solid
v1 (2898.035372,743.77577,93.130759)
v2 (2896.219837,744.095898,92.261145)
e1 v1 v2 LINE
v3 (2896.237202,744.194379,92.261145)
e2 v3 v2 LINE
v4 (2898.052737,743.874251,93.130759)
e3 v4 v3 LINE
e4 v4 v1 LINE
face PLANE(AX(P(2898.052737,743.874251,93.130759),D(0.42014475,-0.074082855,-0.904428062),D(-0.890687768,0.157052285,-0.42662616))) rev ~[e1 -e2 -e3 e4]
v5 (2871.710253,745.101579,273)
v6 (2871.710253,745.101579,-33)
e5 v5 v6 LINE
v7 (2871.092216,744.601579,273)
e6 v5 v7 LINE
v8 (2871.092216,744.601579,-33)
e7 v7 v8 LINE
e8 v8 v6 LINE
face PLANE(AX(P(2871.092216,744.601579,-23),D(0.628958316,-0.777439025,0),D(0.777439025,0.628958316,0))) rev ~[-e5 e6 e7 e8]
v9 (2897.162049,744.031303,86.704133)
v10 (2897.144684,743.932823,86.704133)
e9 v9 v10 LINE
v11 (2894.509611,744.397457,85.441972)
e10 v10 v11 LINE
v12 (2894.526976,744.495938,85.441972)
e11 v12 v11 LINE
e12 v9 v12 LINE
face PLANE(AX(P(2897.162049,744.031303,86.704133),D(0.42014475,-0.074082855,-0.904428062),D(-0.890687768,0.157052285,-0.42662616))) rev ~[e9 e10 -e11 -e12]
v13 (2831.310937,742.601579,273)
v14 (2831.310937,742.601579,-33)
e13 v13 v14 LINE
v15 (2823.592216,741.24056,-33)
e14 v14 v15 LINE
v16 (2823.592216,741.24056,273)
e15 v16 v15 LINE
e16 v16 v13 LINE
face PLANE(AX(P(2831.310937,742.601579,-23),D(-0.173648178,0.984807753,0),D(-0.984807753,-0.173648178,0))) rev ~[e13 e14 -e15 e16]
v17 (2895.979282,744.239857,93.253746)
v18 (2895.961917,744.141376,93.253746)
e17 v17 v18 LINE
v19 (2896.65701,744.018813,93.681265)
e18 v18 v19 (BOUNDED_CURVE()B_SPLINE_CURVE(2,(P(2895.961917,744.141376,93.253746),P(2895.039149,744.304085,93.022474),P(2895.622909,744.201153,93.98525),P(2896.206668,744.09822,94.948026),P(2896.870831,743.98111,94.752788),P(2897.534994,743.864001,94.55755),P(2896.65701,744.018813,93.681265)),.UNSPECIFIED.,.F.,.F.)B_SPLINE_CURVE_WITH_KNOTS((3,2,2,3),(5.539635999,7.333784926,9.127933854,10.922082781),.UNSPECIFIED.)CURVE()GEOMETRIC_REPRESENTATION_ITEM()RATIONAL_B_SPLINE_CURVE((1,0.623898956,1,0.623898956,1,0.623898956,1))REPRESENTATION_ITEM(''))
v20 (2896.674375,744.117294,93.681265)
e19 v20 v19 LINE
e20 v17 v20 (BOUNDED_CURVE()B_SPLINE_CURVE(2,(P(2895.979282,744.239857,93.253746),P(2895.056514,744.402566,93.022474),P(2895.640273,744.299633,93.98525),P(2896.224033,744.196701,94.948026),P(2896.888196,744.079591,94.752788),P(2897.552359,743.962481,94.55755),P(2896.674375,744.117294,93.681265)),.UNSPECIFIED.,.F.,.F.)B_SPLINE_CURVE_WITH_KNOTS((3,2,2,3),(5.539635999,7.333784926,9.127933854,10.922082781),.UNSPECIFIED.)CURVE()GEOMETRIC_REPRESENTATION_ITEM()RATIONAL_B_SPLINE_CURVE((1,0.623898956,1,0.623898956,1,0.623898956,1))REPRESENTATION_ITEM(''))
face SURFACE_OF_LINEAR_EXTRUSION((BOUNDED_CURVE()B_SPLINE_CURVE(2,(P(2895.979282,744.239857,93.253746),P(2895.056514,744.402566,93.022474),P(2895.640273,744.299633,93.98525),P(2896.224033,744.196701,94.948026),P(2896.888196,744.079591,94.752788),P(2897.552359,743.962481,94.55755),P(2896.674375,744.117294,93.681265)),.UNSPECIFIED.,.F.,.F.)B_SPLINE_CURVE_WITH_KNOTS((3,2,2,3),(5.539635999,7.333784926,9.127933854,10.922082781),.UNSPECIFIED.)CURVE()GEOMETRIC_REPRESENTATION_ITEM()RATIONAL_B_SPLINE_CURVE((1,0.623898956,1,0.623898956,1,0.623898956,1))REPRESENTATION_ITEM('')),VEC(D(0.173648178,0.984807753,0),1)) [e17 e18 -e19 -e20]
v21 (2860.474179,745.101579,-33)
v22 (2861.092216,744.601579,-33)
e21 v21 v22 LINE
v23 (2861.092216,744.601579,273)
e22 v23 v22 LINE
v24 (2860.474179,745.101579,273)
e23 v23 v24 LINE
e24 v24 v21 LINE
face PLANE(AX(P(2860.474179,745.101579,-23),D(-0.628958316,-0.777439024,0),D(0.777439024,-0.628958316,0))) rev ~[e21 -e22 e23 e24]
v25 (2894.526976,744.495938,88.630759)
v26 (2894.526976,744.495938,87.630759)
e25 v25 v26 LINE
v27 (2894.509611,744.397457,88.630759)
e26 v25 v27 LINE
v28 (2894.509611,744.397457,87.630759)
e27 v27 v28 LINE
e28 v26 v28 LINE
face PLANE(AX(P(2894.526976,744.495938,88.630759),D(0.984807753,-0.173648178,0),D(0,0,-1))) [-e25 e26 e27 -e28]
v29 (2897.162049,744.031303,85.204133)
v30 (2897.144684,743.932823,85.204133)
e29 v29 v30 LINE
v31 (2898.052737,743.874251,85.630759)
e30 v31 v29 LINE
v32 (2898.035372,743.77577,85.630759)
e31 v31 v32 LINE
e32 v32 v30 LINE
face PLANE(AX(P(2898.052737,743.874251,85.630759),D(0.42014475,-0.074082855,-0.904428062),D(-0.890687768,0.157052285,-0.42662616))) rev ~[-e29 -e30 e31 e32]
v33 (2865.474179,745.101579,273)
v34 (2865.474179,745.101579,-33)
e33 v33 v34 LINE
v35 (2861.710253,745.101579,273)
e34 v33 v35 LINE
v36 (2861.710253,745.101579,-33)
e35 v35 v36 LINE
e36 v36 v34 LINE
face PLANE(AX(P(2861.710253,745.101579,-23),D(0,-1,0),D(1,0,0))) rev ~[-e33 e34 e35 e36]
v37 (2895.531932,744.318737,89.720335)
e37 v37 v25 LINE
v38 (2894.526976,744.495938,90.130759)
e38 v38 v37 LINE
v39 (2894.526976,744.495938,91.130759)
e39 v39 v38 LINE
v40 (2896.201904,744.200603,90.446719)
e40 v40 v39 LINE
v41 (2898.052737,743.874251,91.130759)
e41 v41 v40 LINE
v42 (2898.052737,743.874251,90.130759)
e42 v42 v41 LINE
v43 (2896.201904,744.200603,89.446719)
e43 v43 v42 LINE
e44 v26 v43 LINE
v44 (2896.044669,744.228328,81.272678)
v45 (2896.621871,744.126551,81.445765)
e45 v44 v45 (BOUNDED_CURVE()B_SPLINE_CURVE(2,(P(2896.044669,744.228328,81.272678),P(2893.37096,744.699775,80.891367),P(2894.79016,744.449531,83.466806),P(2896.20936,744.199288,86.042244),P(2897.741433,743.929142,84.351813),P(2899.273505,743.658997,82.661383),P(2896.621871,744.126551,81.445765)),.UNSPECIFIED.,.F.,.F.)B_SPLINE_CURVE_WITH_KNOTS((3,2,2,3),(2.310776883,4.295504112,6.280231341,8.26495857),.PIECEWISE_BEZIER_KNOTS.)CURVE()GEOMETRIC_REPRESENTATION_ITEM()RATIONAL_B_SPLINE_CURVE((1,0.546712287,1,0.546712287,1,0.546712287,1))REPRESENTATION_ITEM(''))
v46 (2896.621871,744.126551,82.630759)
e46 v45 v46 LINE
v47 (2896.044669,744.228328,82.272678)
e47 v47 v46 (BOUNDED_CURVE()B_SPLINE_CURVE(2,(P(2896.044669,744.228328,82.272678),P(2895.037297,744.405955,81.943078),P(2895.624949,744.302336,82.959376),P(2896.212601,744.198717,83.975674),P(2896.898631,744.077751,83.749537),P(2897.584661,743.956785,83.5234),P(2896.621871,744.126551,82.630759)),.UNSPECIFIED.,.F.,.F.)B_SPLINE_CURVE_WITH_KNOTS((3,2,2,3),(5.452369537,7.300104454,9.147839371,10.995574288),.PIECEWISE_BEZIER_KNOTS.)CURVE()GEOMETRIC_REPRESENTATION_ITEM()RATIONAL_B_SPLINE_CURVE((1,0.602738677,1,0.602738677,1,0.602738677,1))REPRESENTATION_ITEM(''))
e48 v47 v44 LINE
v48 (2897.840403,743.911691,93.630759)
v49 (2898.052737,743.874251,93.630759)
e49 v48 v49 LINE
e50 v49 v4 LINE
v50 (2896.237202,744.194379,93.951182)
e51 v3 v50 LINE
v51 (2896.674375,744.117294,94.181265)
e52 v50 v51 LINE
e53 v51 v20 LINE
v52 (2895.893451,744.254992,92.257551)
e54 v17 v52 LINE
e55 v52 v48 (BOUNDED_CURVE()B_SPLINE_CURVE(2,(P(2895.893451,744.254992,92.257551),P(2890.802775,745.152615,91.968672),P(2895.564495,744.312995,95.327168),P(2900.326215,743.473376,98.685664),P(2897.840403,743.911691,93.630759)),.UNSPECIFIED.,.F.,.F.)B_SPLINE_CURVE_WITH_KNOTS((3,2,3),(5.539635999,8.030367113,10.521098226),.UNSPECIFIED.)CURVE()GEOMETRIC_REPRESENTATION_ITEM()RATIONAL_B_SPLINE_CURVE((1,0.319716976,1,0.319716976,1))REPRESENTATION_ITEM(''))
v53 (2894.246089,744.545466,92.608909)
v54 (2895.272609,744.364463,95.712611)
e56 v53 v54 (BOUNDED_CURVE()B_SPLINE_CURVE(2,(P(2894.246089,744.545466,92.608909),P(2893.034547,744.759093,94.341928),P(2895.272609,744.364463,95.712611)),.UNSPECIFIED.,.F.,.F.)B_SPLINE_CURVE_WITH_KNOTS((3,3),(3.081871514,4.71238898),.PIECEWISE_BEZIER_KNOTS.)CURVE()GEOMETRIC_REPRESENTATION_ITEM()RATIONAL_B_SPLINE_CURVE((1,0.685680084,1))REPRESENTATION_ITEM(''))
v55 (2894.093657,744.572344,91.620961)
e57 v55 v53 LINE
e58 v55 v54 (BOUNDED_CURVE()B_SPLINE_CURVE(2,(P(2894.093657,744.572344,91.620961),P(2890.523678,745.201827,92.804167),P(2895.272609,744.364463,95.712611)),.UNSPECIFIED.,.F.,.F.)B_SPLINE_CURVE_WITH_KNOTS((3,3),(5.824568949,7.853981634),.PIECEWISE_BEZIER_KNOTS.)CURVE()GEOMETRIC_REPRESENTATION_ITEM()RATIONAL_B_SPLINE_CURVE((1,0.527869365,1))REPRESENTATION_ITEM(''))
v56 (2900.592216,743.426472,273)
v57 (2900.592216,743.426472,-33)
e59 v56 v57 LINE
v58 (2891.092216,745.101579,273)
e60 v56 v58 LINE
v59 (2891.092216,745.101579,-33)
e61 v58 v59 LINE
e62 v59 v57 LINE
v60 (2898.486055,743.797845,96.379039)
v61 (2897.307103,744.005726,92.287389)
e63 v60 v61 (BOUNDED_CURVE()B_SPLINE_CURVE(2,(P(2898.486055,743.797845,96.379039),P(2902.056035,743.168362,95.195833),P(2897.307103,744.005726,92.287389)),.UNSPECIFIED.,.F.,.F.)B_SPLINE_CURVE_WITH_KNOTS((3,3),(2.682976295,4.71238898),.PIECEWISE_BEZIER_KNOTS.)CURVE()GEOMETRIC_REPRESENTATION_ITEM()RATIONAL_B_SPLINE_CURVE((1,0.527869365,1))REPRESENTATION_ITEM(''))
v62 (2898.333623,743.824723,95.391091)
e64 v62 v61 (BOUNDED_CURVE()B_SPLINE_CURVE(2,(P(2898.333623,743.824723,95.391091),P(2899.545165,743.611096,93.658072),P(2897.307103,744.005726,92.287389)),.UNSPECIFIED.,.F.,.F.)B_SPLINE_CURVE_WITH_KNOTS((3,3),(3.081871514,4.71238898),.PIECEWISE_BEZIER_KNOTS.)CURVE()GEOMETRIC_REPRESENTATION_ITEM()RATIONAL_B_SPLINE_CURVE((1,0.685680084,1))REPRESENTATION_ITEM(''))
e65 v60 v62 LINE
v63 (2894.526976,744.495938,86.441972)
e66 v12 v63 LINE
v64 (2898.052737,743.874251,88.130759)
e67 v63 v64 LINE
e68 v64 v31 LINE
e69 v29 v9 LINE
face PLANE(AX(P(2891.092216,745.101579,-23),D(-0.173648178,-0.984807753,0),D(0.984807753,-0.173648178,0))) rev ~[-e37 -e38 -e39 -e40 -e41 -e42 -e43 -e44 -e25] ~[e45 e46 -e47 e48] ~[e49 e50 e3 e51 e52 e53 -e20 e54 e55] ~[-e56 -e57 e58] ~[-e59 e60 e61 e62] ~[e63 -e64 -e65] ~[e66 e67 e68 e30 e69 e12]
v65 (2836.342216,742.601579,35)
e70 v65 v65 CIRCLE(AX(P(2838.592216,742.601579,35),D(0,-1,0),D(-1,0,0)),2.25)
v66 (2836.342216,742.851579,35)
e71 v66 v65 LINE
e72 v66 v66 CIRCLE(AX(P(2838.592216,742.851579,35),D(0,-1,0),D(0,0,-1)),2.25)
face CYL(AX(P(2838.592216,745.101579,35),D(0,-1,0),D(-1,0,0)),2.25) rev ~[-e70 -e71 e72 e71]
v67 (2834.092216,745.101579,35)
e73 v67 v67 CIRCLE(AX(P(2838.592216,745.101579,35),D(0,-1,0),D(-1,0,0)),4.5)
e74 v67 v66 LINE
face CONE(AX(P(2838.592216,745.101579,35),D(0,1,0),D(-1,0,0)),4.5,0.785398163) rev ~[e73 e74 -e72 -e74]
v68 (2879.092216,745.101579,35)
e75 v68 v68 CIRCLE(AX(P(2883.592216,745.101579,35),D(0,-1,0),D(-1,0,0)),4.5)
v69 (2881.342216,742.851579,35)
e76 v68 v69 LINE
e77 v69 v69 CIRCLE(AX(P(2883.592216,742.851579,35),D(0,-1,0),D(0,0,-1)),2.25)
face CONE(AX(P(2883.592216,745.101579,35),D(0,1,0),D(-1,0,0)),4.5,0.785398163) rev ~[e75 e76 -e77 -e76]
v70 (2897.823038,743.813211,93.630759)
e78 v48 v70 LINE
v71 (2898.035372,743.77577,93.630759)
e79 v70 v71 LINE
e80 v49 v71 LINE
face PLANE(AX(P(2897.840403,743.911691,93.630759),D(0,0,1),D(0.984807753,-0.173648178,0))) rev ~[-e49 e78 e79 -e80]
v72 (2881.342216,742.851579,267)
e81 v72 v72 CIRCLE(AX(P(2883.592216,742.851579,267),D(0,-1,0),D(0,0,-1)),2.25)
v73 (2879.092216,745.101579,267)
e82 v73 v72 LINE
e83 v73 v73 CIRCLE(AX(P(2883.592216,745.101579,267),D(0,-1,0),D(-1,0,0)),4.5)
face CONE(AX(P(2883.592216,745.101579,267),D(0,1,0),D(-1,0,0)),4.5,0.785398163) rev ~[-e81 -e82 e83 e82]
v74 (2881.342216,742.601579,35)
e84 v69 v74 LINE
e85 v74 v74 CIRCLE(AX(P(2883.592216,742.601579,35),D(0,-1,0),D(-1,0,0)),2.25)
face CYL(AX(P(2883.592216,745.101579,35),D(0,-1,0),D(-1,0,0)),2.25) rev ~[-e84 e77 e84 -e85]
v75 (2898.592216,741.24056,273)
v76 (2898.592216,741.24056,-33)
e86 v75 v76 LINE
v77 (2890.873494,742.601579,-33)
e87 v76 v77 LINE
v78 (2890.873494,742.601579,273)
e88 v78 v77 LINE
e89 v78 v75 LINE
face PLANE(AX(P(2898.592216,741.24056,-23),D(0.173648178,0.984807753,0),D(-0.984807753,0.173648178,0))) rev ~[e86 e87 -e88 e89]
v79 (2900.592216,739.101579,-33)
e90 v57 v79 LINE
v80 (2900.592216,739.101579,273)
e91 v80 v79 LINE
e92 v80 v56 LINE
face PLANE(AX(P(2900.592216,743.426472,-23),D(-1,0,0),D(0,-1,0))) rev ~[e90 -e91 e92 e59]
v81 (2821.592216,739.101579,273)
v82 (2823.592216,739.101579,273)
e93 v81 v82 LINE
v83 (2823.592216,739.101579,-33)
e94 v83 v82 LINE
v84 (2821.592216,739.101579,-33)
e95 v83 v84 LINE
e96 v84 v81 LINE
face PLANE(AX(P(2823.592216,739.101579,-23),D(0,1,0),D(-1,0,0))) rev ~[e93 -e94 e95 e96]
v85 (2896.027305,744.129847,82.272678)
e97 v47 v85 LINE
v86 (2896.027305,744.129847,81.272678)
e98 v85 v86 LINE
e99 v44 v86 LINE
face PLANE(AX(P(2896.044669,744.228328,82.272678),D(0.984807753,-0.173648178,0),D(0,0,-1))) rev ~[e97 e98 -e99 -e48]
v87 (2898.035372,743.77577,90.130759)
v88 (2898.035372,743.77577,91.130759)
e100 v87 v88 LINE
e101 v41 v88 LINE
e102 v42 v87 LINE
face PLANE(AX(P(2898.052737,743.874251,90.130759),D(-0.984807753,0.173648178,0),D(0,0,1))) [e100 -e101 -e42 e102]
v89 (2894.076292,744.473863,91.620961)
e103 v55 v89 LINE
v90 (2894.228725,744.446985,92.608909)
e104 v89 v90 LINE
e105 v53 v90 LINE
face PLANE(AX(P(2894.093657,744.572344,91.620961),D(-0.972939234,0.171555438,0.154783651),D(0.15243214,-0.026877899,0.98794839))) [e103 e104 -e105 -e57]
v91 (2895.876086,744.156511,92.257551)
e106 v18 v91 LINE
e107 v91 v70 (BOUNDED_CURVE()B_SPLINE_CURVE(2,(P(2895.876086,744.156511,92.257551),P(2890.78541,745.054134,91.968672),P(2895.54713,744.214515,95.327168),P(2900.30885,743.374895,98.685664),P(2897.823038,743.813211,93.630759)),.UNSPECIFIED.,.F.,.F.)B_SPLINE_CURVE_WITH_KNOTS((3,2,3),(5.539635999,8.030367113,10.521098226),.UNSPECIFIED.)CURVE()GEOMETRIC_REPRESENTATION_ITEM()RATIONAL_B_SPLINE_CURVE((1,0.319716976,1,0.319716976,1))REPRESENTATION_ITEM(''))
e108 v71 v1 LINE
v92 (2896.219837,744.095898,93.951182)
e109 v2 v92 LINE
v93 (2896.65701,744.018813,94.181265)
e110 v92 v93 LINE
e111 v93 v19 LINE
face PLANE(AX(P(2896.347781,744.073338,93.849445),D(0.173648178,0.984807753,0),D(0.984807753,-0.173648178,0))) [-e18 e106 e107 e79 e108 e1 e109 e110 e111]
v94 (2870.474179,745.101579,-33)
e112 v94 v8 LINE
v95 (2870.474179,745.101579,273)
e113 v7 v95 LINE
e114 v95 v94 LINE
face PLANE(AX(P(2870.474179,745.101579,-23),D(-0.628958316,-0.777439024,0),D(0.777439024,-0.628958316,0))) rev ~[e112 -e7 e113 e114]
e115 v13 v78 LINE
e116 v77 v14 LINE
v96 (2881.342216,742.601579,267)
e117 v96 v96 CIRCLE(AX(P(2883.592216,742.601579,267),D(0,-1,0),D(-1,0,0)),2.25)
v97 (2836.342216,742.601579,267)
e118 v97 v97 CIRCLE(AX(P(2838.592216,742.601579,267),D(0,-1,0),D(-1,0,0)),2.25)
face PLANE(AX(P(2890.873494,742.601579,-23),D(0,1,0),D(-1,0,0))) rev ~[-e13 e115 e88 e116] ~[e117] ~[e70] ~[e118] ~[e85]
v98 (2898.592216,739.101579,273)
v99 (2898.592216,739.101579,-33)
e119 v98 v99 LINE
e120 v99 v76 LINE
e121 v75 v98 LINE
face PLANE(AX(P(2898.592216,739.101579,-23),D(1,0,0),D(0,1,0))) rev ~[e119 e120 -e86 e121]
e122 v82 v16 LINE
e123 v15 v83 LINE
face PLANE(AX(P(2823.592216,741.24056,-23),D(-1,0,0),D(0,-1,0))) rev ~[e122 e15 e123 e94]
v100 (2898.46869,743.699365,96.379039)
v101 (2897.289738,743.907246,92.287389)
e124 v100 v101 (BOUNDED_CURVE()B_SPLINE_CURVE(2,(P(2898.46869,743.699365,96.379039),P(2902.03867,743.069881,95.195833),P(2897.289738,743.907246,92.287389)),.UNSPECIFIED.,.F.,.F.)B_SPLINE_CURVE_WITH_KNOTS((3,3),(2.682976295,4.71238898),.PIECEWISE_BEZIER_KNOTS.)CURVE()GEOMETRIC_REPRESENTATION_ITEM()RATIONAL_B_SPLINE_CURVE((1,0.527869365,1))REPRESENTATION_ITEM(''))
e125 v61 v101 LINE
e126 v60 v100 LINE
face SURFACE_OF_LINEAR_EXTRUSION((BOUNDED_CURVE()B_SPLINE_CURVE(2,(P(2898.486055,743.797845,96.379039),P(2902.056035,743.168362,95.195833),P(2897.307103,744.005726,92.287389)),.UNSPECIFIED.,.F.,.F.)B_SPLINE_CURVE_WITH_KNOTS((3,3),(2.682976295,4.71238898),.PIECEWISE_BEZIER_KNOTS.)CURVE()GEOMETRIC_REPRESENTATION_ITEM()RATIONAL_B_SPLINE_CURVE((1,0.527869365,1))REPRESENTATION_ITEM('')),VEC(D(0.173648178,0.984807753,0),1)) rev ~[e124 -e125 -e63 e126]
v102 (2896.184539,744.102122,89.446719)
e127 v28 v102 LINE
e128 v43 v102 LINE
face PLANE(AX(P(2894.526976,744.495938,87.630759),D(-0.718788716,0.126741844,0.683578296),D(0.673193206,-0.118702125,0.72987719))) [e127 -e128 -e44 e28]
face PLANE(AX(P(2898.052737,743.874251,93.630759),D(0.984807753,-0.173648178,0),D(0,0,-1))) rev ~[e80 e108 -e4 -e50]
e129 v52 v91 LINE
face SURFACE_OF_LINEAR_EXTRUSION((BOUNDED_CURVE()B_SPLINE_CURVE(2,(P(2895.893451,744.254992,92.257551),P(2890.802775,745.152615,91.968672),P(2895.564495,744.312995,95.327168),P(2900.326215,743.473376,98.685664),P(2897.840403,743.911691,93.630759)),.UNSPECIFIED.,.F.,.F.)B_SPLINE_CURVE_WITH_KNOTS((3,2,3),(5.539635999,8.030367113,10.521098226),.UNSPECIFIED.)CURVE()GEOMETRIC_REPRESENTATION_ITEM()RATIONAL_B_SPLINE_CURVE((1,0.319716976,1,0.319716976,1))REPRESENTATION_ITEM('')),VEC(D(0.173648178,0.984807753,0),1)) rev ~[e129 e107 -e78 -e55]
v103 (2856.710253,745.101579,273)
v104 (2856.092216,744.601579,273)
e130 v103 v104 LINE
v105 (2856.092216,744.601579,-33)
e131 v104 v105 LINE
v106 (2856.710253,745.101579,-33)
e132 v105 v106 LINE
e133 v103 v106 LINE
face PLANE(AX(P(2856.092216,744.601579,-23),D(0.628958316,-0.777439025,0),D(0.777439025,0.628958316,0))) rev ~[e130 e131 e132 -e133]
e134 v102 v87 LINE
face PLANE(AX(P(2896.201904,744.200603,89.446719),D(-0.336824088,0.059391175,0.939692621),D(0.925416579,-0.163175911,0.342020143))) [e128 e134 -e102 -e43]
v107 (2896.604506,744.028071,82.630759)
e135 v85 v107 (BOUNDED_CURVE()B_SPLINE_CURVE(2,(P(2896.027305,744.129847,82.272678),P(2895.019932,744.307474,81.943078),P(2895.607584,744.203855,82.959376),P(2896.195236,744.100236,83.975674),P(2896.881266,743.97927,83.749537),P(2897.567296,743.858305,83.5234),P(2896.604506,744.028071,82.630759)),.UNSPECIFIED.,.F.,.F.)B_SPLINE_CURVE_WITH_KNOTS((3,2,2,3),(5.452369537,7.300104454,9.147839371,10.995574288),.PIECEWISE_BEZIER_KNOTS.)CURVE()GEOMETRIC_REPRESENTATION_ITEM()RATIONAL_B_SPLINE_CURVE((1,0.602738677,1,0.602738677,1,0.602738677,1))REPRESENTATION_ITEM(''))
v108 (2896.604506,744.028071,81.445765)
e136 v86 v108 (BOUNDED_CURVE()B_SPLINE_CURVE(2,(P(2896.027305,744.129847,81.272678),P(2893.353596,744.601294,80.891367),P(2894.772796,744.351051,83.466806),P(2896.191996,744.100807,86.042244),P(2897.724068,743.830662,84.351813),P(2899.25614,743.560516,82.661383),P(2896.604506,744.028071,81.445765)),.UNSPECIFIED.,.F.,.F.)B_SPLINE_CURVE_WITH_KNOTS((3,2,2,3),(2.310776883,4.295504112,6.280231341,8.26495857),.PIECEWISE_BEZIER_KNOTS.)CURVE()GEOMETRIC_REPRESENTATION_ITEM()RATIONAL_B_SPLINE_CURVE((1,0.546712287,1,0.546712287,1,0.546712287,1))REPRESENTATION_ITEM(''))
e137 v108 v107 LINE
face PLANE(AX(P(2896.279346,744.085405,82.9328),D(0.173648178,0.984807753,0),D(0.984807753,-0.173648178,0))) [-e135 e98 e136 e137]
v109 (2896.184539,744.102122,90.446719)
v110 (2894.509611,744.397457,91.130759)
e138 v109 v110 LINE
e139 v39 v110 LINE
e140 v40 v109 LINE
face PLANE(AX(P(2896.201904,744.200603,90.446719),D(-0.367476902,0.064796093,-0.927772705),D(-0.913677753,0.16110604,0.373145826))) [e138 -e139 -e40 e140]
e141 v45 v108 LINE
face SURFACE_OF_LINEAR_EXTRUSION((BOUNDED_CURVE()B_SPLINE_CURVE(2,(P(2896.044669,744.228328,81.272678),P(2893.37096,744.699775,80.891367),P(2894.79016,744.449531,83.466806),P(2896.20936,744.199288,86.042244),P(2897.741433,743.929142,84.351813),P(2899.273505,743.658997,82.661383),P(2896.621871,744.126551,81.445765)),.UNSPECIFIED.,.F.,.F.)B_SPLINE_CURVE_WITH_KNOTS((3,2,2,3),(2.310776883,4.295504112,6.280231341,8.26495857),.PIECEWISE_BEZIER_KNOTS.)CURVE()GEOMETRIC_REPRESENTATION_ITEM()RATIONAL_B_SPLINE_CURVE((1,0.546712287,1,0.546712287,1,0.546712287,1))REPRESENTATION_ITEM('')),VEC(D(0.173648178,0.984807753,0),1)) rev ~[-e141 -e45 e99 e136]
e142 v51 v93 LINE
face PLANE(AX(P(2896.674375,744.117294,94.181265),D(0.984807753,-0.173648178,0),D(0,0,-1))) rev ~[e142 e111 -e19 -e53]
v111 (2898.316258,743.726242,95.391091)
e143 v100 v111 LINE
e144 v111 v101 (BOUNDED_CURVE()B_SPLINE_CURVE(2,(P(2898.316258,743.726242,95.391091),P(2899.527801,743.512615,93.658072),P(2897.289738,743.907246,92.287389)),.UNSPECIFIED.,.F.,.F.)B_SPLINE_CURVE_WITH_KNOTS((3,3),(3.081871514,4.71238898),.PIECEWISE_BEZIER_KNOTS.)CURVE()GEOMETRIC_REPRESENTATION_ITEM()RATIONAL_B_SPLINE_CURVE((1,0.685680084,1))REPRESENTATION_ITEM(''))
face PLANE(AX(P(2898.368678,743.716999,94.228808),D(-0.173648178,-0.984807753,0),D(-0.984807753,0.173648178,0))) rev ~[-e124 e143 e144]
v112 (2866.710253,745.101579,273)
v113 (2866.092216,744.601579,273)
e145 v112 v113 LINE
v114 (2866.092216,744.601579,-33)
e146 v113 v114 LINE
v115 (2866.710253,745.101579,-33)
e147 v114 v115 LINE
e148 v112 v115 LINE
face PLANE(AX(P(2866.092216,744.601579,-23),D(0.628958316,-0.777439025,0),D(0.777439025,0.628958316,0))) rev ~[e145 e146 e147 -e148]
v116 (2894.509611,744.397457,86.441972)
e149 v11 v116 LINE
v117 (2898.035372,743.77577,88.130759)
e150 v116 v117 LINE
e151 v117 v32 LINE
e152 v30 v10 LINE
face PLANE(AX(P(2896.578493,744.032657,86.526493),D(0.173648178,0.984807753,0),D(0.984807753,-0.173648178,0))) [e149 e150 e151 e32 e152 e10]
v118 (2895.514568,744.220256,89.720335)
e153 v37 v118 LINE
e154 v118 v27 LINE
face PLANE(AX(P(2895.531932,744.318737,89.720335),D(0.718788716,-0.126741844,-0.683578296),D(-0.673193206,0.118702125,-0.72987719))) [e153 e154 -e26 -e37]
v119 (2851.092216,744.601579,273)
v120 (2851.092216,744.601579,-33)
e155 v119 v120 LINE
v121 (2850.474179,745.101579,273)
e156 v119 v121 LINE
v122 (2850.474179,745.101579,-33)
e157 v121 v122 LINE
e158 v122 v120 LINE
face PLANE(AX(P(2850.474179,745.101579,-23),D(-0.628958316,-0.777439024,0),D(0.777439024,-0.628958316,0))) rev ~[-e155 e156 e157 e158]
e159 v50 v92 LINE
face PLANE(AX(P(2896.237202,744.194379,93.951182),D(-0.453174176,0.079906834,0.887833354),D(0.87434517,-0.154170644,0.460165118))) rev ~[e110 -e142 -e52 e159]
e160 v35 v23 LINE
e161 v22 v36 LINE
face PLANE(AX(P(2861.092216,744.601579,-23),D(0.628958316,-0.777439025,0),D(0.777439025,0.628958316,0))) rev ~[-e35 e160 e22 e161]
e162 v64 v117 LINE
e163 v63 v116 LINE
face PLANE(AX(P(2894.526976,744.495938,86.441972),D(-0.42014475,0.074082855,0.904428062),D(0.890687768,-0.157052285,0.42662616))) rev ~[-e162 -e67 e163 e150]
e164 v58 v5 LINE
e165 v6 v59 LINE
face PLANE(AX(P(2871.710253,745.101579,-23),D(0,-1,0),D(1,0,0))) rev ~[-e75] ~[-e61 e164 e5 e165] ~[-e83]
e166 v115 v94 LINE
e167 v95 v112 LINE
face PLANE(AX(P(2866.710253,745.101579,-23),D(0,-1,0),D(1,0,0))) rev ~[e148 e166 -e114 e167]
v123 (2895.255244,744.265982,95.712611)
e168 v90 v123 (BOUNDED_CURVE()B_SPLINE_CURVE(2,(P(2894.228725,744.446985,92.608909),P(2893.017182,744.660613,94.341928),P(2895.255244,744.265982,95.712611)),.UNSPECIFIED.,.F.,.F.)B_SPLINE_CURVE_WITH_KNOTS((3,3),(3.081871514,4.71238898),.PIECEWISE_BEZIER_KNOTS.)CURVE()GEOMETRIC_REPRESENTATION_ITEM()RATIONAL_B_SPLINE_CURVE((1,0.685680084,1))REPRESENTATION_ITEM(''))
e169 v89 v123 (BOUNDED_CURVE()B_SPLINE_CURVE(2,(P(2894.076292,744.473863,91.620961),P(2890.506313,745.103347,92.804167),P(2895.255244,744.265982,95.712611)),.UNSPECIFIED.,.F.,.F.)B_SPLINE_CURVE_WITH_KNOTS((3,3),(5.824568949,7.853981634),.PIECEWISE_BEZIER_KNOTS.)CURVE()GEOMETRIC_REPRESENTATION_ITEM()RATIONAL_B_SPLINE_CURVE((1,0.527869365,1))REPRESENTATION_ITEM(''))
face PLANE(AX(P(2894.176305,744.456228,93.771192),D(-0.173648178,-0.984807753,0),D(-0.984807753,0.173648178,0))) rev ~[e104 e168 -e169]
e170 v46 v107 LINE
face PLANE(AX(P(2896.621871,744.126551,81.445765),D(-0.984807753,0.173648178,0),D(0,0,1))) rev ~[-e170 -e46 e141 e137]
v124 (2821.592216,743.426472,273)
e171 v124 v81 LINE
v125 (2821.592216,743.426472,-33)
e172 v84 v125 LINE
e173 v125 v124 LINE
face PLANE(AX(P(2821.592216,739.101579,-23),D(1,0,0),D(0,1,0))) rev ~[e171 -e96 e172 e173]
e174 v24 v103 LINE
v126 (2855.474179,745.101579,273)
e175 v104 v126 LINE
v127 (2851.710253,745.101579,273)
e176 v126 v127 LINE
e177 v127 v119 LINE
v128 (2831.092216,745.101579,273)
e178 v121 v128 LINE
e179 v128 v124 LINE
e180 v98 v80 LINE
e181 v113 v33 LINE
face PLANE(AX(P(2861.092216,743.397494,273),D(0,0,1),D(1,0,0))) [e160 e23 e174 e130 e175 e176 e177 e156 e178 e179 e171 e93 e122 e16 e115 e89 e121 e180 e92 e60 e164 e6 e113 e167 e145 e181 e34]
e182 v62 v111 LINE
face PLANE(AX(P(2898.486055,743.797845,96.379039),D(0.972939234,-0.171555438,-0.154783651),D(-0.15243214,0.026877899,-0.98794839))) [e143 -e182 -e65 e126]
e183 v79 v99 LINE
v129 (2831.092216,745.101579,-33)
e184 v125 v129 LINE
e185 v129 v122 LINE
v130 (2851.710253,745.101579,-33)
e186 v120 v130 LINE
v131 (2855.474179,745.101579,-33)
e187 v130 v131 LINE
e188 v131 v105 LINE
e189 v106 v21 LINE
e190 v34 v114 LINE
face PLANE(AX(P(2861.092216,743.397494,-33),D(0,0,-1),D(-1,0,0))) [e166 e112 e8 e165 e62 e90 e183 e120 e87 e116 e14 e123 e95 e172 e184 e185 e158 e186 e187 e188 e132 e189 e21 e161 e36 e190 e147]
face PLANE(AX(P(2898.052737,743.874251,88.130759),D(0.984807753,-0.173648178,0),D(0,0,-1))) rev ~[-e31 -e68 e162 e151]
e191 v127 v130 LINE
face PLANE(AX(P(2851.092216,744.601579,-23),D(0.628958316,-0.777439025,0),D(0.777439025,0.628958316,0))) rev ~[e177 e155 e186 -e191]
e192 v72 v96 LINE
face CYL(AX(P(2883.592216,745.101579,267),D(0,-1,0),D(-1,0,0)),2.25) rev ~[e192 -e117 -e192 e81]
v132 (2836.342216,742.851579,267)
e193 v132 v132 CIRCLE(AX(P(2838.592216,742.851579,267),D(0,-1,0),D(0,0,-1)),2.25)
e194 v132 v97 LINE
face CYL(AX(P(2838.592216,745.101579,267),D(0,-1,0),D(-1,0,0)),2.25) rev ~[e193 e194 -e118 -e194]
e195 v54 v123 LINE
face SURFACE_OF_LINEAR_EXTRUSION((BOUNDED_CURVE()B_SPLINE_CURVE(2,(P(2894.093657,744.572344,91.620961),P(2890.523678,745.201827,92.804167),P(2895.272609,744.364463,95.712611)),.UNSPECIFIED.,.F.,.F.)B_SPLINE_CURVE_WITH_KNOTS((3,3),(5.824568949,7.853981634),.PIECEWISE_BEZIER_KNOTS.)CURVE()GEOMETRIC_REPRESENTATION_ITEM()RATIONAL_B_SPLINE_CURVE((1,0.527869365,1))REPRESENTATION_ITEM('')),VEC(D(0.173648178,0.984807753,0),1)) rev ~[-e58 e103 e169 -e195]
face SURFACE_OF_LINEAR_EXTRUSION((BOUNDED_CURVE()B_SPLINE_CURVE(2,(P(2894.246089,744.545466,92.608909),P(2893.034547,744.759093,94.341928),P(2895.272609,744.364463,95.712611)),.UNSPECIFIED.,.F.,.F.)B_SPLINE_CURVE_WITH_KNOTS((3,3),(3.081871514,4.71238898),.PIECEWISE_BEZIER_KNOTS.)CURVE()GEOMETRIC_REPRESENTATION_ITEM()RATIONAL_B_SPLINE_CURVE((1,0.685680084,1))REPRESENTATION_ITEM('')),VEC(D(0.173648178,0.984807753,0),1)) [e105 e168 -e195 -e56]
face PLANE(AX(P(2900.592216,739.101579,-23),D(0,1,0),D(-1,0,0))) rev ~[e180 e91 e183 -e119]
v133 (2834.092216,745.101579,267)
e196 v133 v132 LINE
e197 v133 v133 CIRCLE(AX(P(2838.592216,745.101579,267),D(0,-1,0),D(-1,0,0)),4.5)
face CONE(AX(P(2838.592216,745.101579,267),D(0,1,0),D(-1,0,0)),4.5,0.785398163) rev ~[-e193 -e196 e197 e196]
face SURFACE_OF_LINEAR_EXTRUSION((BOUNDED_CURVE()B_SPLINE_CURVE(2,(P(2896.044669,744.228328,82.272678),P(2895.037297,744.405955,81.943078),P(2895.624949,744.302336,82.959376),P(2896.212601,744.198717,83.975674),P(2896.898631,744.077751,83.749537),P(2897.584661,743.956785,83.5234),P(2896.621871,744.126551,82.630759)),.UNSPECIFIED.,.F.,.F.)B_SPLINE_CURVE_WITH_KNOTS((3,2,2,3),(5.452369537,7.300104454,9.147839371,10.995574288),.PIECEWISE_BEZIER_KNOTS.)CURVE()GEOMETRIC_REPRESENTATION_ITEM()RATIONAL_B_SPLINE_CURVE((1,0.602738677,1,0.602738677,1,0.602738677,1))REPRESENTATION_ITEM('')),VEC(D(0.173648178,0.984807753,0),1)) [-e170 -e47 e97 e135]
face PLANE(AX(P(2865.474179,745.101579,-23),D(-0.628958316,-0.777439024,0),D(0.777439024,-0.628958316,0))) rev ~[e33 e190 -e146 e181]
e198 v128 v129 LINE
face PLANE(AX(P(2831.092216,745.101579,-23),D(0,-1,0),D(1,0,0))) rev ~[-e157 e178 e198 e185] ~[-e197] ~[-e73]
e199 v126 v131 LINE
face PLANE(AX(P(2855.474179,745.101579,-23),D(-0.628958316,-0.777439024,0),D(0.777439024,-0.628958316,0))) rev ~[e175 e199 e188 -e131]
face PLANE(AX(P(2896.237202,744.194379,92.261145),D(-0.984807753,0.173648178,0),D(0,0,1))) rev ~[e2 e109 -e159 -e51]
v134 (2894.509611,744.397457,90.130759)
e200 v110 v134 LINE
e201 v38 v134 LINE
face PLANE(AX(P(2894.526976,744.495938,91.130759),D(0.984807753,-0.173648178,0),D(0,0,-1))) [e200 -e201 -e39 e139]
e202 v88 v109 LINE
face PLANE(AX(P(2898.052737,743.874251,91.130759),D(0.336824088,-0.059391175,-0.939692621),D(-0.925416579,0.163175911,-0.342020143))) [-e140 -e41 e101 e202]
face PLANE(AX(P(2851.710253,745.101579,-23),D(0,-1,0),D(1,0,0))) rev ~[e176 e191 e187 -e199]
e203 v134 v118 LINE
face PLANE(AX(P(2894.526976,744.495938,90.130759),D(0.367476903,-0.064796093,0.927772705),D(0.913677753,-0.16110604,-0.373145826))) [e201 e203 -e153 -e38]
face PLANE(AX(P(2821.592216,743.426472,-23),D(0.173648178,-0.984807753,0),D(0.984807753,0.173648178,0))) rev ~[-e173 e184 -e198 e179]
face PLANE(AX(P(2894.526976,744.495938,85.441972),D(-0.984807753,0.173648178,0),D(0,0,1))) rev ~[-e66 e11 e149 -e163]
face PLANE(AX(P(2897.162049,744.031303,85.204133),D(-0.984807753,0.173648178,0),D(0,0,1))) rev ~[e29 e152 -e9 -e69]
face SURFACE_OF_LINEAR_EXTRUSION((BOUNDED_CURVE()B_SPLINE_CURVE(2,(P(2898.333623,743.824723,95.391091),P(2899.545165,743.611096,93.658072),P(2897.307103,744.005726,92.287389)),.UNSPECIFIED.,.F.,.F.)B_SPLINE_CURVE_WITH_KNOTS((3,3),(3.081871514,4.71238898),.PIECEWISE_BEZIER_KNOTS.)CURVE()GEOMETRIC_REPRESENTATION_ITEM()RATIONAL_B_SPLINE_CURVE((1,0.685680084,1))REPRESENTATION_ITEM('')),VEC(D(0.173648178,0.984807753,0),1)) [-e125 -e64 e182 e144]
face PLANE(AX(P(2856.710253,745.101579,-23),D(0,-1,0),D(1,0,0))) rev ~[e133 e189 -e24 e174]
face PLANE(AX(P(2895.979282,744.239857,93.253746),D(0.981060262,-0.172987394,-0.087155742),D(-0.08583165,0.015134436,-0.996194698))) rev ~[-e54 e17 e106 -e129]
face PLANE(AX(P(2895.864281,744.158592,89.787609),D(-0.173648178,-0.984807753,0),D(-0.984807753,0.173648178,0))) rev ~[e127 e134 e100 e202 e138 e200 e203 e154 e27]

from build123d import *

# Parameters (mm, degrees)
EXTRUDE_1_DEPTH           = 250
CUT_EXTRUDE_1_DEPTH       = 0.1
EXTRUDE_2_DEPTH           = 23
EXTRUDE_3_DEPTH           = 23
HOLE_WIZARD_0_D           = 4.5
HOLE_WIZARD_0_CSINK_D     = 9
HOLE_WIZARD_0_CSINK_ANGLE = 90
EXTRUDE_4_DEPTH           = 10


with BuildPart() as part:
    # Model → 凸台-拉伸1 (new body)
    with BuildSketch(Plane.XY):
        Polygon((2831.092215663, 745.101578786), (2821.592215663, 743.426472469), (2821.592215663, 739.101578786), (2823.592215663, 739.101578786), (2823.592215663, 741.240559901), (2831.310937322, 742.601578786), (2890.873494004, 742.601578786), (2898.592215663, 741.240559901), (2898.592215663, 739.101578786), (2900.592215663, 739.101578786), (2900.592215663, 743.426472469), (2891.092215663, 745.101578786), (2871.710252666, 745.101578786), (2871.092215663, 744.601578786), (2870.474178661, 745.101578786), (2866.710252666, 745.101578786), (2866.092215663, 744.601578786), (2865.474178661, 745.101578786), (2861.710252666, 745.101578786), (2861.092215663, 744.601578786), (2860.474178661, 745.101578786), (2856.710252666, 745.101578786), (2856.092215663, 744.601578786), (2855.474178661, 745.101578786), (2851.710252666, 745.101578786), (2851.092215663, 744.601578786), (2850.474178661, 745.101578786), align=None)
    extrude(amount=EXTRUDE_1_DEPTH)

    # 草图1 → 切除-拉伸1 (cut)
    with BuildSketch(Plane(origin=(214.596971693, 1217.039904055, 0), x_dir=(0.9848077530109746, -0.1736481776739262, 0), z_dir=(0.17364817767392618, 0.9848077530109745, 0))):
        with BuildLine():
            Line((2722.813350585, -82.272677588), (2722.813350585, -81.272677588))
            add(Edge.make_bspline(
                [(2722.813350585, -81.272677588), (2720.098395425, -80.891367095), (2721.539488829, -83.466805597), (2722.980582232, -86.042244099), (2724.536289142, -84.351813392), (2726.091996051, -82.661382685), (2723.399456691, -81.445765021)],
                knots=[2.310776883, 2.310776883, 2.310776883, 4.295504112, 4.295504112, 6.280231341, 6.280231341, 8.26495857, 8.26495857, 8.26495857], degree=2, weights=[1, 0.546712287, 1, 0.546712287, 1, 0.546712287, 1]))
            Line((2723.399456691, -81.445765021), (2723.399456691, -82.630759165))
            add(Edge.make_bspline(
                [(2722.813350585, -82.272677588), (2721.79043745, -81.943078281), (2722.387154928, -82.959375958), (2722.983872407, -83.975673634), (2723.680485897, -83.749536627), (2724.377099386, -83.523399621), (2723.399456691, -82.630759165)],
                knots=[5.452369537, 5.452369537, 5.452369537, 7.300104454, 7.300104454, 9.147839371, 9.147839371, 10.995574288, 10.995574288, 10.995574288], degree=2, weights=[1, 0.602738677, 1, 0.602738677, 1, 0.602738677, 1]))
        make_face()
        Polygon((2723.947967705, -86.704133005), (2721.272244062, -85.441972142), (2721.272244062, -86.441972142), (2724.852395767, -88.130759165), (2724.852395767, -85.630759165), (2723.947967705, -85.204133005), align=None)
        Polygon((2722.973010525, -89.446718879), (2724.852395767, -90.130759165), (2724.852395767, -91.130759165), (2722.973010525, -90.446718879), (2721.272244062, -91.130759165), (2721.272244062, -90.130759165), (2722.29270394, -89.720334993), (2721.272244062, -88.630759165), (2721.272244062, -87.630759165), align=None)
        with BuildLine():
            Line((2722.746954699, -93.253746163), (2722.659798957, -92.257551464))
            add(Edge.make_bspline(
                [(2722.659798957, -92.257551464), (2717.490591073, -91.968672054), (2722.325768389, -95.327168138), (2727.160945704, -98.685664222), (2724.636785845, -93.630759165)],
                knots=[5.539635999, 5.539635999, 5.539635999, 8.030367113, 8.030367113, 10.521098226, 10.521098226, 10.521098226], degree=2, weights=[1, 0.319716976, 1, 0.319716976, 1]))
            Line((2724.636785845, -93.630759165), (2724.852395767, -93.630759165))
            Line((2724.852395767, -93.630759165), (2724.852395767, -93.130759165))
            Line((2724.852395767, -93.130759165), (2723.008853275, -92.261145))
            Line((2723.008853275, -92.261145), (2723.008853275, -93.951182078))
            Line((2723.008853275, -93.951182078), (2723.452769952, -94.181264637))
            Line((2723.452769952, -94.181264637), (2723.452769952, -93.681264637))
            add(Edge.make_bspline(
                [(2722.746954699, -93.253746163), (2721.809951026, -93.022473901), (2722.402716181, -93.98524995), (2722.995481336, -94.948025999), (2723.669889827, -94.752788115), (2724.344298318, -94.557550231), (2723.452769952, -93.681264637)],
                knots=[5.539635999, 5.539635999, 5.539635999, 7.333784926, 7.333784926, 9.127933854, 9.127933854, 10.922082781, 10.922082781, 10.922082781], degree=2, weights=[1, 0.623898956, 1, 0.623898956, 1, 0.623898956, 1]))
        make_face()
        with BuildLine():
            add(Edge.make_bspline(
                [(2720.98702462, -92.608909027), (2719.756792423, -94.341927995), (2722.029380258, -95.712610775)],
                knots=[3.081871514, 3.081871514, 3.081871514, 4.71238898, 4.71238898, 4.71238898], degree=2, weights=[1, 0.685680084, 1]))
            add(Edge.make_bspline(
                [(2720.832240969, -91.620960637), (2717.207188633, -92.804166525), (2722.029380258, -95.712610775)],
                knots=[5.824568949, 5.824568949, 5.824568949, 7.853981634, 7.853981634, 7.853981634], degree=2, weights=[1, 0.527869365, 1]))
            Line((2720.832240969, -91.620960637), (2720.98702462, -92.608909027))
        make_face()
        with BuildLine():
            add(Edge.make_bspline(
                [(2725.137615209, -95.391090973), (2726.367847406, -93.658072005), (2724.095259571, -92.287389225)],
                knots=[3.081871514, 3.081871514, 3.081871514, 4.71238898, 4.71238898, 4.71238898], degree=2, weights=[1, 0.685680084, 1]))
            add(Edge.make_bspline(
                [(2725.29239886, -96.379039363), (2728.917451195, -95.195833475), (2724.095259571, -92.287389225)],
                knots=[2.682976295, 2.682976295, 2.682976295, 4.71238898, 4.71238898, 4.71238898], degree=2, weights=[1, 0.527869365, 1]))
            Line((2725.29239886, -96.379039363), (2725.137615209, -95.391090973))
        make_face()
    extrude(amount=-CUT_EXTRUDE_1_DEPTH, mode=Mode.SUBTRACT)

    # 草图4 → 凸台-拉伸2 (add)
    with BuildSketch(Plane.XY.offset(250)):
        Polygon((2850.474178661, 745.101578786), (2831.092215663, 745.101578786), (2821.592215663, 743.426472469), (2821.592215663, 739.101578786), (2823.592215663, 739.101578786), (2823.592215663, 741.240559901), (2831.310937322, 742.601578786), (2890.873494004, 742.601578786), (2898.592215663, 741.240559901), (2898.592215663, 739.101578786), (2900.592215663, 739.101578786), (2900.592215663, 743.426472469), (2891.092215663, 745.101578786), (2871.710252666, 745.101578786), (2871.092215663, 744.601578786), (2870.474178661, 745.101578786), (2866.710252666, 745.101578786), (2866.092215663, 744.601578786), (2865.474178661, 745.101578786), (2861.710252666, 745.101578786), (2861.092215663, 744.601578786), (2860.474178661, 745.101578786), (2856.710252666, 745.101578786), (2856.092215663, 744.601578786), (2855.474178661, 745.101578786), (2851.710252666, 745.101578786), (2851.092215663, 744.601578786), align=None)
    extrude(amount=EXTRUDE_2_DEPTH)

    # 草图5 → 凸台-拉伸3 (add)
    with BuildSketch(Plane(origin=(0, 0, 0), x_dir=(-1, 0, 0), z_dir=(0, 0, -1))):
        Polygon((-2831.092215663, 745.101578786), (-2850.474178661, 745.101578786), (-2851.092215663, 744.601578786), (-2851.710252666, 745.101578786), (-2855.474178661, 745.101578786), (-2856.092215663, 744.601578786), (-2856.710252666, 745.101578786), (-2860.474178661, 745.101578786), (-2861.092215663, 744.601578786), (-2861.710252666, 745.101578786), (-2865.474178661, 745.101578786), (-2866.092215663, 744.601578786), (-2866.710252666, 745.101578786), (-2870.474178661, 745.101578786), (-2871.092215663, 744.601578786), (-2871.710252666, 745.101578786), (-2891.092215663, 745.101578786), (-2900.592215663, 743.426472469), (-2900.592215663, 739.101578786), (-2898.592215663, 739.101578786), (-2898.592215663, 741.240559901), (-2890.873494004, 742.601578786), (-2831.310937322, 742.601578786), (-2823.592215663, 741.240559901), (-2823.592215663, 739.101578786), (-2821.592215663, 739.101578786), (-2821.592215663, 743.426472469), align=None)
    extrude(amount=EXTRUDE_3_DEPTH)

    # 打孔尺寸(%根据)开槽半沉头木螺钉的类型0 (through all)
    with Locations(Plane(origin=(0, 745.101578786, 0), x_dir=(1, 0, 0), z_dir=(0, 1, 0))):
        with Locations((2883.592215663, -267), (2838.592215663, -267), (2838.592215663, -35), (2883.592215663, -35)):
            CounterSinkHole(HOLE_WIZARD_0_D / 2, HOLE_WIZARD_0_CSINK_D / 2, counter_sink_angle=HOLE_WIZARD_0_CSINK_ANGLE)

    # 草图10 → 凸台-拉伸4 (add)
    with BuildSketch(Plane(origin=(0, 0, -23), x_dir=(-1, 0, 0), z_dir=(0, 0, -1))):
        Polygon((-2821.592215663, 743.426472469), (-2831.092215663, 745.101578786), (-2850.474178661, 745.101578786), (-2851.092215663, 744.601578786), (-2851.710252666, 745.101578786), (-2855.474178661, 745.101578786), (-2856.092215663, 744.601578786), (-2856.710252666, 745.101578786), (-2860.474178661, 745.101578786), (-2861.092215663, 744.601578786), (-2861.710252666, 745.101578786), (-2865.474178661, 745.101578786), (-2866.092215663, 744.601578786), (-2866.710252666, 745.101578786), (-2870.474178661, 745.101578786), (-2871.092215663, 744.601578786), (-2871.710252666, 745.101578786), (-2891.092215663, 745.101578786), (-2900.592215663, 743.426472469), (-2900.592215663, 739.101578786), (-2898.592215663, 739.101578786), (-2898.592215663, 741.240559901), (-2890.873494004, 742.601578786), (-2831.310937322, 742.601578786), (-2823.592215663, 741.240559901), (-2823.592215663, 739.101578786), (-2821.592215663, 739.101578786), align=None)
    extrude(amount=EXTRUDE_4_DEPTH)


solid = part.part
